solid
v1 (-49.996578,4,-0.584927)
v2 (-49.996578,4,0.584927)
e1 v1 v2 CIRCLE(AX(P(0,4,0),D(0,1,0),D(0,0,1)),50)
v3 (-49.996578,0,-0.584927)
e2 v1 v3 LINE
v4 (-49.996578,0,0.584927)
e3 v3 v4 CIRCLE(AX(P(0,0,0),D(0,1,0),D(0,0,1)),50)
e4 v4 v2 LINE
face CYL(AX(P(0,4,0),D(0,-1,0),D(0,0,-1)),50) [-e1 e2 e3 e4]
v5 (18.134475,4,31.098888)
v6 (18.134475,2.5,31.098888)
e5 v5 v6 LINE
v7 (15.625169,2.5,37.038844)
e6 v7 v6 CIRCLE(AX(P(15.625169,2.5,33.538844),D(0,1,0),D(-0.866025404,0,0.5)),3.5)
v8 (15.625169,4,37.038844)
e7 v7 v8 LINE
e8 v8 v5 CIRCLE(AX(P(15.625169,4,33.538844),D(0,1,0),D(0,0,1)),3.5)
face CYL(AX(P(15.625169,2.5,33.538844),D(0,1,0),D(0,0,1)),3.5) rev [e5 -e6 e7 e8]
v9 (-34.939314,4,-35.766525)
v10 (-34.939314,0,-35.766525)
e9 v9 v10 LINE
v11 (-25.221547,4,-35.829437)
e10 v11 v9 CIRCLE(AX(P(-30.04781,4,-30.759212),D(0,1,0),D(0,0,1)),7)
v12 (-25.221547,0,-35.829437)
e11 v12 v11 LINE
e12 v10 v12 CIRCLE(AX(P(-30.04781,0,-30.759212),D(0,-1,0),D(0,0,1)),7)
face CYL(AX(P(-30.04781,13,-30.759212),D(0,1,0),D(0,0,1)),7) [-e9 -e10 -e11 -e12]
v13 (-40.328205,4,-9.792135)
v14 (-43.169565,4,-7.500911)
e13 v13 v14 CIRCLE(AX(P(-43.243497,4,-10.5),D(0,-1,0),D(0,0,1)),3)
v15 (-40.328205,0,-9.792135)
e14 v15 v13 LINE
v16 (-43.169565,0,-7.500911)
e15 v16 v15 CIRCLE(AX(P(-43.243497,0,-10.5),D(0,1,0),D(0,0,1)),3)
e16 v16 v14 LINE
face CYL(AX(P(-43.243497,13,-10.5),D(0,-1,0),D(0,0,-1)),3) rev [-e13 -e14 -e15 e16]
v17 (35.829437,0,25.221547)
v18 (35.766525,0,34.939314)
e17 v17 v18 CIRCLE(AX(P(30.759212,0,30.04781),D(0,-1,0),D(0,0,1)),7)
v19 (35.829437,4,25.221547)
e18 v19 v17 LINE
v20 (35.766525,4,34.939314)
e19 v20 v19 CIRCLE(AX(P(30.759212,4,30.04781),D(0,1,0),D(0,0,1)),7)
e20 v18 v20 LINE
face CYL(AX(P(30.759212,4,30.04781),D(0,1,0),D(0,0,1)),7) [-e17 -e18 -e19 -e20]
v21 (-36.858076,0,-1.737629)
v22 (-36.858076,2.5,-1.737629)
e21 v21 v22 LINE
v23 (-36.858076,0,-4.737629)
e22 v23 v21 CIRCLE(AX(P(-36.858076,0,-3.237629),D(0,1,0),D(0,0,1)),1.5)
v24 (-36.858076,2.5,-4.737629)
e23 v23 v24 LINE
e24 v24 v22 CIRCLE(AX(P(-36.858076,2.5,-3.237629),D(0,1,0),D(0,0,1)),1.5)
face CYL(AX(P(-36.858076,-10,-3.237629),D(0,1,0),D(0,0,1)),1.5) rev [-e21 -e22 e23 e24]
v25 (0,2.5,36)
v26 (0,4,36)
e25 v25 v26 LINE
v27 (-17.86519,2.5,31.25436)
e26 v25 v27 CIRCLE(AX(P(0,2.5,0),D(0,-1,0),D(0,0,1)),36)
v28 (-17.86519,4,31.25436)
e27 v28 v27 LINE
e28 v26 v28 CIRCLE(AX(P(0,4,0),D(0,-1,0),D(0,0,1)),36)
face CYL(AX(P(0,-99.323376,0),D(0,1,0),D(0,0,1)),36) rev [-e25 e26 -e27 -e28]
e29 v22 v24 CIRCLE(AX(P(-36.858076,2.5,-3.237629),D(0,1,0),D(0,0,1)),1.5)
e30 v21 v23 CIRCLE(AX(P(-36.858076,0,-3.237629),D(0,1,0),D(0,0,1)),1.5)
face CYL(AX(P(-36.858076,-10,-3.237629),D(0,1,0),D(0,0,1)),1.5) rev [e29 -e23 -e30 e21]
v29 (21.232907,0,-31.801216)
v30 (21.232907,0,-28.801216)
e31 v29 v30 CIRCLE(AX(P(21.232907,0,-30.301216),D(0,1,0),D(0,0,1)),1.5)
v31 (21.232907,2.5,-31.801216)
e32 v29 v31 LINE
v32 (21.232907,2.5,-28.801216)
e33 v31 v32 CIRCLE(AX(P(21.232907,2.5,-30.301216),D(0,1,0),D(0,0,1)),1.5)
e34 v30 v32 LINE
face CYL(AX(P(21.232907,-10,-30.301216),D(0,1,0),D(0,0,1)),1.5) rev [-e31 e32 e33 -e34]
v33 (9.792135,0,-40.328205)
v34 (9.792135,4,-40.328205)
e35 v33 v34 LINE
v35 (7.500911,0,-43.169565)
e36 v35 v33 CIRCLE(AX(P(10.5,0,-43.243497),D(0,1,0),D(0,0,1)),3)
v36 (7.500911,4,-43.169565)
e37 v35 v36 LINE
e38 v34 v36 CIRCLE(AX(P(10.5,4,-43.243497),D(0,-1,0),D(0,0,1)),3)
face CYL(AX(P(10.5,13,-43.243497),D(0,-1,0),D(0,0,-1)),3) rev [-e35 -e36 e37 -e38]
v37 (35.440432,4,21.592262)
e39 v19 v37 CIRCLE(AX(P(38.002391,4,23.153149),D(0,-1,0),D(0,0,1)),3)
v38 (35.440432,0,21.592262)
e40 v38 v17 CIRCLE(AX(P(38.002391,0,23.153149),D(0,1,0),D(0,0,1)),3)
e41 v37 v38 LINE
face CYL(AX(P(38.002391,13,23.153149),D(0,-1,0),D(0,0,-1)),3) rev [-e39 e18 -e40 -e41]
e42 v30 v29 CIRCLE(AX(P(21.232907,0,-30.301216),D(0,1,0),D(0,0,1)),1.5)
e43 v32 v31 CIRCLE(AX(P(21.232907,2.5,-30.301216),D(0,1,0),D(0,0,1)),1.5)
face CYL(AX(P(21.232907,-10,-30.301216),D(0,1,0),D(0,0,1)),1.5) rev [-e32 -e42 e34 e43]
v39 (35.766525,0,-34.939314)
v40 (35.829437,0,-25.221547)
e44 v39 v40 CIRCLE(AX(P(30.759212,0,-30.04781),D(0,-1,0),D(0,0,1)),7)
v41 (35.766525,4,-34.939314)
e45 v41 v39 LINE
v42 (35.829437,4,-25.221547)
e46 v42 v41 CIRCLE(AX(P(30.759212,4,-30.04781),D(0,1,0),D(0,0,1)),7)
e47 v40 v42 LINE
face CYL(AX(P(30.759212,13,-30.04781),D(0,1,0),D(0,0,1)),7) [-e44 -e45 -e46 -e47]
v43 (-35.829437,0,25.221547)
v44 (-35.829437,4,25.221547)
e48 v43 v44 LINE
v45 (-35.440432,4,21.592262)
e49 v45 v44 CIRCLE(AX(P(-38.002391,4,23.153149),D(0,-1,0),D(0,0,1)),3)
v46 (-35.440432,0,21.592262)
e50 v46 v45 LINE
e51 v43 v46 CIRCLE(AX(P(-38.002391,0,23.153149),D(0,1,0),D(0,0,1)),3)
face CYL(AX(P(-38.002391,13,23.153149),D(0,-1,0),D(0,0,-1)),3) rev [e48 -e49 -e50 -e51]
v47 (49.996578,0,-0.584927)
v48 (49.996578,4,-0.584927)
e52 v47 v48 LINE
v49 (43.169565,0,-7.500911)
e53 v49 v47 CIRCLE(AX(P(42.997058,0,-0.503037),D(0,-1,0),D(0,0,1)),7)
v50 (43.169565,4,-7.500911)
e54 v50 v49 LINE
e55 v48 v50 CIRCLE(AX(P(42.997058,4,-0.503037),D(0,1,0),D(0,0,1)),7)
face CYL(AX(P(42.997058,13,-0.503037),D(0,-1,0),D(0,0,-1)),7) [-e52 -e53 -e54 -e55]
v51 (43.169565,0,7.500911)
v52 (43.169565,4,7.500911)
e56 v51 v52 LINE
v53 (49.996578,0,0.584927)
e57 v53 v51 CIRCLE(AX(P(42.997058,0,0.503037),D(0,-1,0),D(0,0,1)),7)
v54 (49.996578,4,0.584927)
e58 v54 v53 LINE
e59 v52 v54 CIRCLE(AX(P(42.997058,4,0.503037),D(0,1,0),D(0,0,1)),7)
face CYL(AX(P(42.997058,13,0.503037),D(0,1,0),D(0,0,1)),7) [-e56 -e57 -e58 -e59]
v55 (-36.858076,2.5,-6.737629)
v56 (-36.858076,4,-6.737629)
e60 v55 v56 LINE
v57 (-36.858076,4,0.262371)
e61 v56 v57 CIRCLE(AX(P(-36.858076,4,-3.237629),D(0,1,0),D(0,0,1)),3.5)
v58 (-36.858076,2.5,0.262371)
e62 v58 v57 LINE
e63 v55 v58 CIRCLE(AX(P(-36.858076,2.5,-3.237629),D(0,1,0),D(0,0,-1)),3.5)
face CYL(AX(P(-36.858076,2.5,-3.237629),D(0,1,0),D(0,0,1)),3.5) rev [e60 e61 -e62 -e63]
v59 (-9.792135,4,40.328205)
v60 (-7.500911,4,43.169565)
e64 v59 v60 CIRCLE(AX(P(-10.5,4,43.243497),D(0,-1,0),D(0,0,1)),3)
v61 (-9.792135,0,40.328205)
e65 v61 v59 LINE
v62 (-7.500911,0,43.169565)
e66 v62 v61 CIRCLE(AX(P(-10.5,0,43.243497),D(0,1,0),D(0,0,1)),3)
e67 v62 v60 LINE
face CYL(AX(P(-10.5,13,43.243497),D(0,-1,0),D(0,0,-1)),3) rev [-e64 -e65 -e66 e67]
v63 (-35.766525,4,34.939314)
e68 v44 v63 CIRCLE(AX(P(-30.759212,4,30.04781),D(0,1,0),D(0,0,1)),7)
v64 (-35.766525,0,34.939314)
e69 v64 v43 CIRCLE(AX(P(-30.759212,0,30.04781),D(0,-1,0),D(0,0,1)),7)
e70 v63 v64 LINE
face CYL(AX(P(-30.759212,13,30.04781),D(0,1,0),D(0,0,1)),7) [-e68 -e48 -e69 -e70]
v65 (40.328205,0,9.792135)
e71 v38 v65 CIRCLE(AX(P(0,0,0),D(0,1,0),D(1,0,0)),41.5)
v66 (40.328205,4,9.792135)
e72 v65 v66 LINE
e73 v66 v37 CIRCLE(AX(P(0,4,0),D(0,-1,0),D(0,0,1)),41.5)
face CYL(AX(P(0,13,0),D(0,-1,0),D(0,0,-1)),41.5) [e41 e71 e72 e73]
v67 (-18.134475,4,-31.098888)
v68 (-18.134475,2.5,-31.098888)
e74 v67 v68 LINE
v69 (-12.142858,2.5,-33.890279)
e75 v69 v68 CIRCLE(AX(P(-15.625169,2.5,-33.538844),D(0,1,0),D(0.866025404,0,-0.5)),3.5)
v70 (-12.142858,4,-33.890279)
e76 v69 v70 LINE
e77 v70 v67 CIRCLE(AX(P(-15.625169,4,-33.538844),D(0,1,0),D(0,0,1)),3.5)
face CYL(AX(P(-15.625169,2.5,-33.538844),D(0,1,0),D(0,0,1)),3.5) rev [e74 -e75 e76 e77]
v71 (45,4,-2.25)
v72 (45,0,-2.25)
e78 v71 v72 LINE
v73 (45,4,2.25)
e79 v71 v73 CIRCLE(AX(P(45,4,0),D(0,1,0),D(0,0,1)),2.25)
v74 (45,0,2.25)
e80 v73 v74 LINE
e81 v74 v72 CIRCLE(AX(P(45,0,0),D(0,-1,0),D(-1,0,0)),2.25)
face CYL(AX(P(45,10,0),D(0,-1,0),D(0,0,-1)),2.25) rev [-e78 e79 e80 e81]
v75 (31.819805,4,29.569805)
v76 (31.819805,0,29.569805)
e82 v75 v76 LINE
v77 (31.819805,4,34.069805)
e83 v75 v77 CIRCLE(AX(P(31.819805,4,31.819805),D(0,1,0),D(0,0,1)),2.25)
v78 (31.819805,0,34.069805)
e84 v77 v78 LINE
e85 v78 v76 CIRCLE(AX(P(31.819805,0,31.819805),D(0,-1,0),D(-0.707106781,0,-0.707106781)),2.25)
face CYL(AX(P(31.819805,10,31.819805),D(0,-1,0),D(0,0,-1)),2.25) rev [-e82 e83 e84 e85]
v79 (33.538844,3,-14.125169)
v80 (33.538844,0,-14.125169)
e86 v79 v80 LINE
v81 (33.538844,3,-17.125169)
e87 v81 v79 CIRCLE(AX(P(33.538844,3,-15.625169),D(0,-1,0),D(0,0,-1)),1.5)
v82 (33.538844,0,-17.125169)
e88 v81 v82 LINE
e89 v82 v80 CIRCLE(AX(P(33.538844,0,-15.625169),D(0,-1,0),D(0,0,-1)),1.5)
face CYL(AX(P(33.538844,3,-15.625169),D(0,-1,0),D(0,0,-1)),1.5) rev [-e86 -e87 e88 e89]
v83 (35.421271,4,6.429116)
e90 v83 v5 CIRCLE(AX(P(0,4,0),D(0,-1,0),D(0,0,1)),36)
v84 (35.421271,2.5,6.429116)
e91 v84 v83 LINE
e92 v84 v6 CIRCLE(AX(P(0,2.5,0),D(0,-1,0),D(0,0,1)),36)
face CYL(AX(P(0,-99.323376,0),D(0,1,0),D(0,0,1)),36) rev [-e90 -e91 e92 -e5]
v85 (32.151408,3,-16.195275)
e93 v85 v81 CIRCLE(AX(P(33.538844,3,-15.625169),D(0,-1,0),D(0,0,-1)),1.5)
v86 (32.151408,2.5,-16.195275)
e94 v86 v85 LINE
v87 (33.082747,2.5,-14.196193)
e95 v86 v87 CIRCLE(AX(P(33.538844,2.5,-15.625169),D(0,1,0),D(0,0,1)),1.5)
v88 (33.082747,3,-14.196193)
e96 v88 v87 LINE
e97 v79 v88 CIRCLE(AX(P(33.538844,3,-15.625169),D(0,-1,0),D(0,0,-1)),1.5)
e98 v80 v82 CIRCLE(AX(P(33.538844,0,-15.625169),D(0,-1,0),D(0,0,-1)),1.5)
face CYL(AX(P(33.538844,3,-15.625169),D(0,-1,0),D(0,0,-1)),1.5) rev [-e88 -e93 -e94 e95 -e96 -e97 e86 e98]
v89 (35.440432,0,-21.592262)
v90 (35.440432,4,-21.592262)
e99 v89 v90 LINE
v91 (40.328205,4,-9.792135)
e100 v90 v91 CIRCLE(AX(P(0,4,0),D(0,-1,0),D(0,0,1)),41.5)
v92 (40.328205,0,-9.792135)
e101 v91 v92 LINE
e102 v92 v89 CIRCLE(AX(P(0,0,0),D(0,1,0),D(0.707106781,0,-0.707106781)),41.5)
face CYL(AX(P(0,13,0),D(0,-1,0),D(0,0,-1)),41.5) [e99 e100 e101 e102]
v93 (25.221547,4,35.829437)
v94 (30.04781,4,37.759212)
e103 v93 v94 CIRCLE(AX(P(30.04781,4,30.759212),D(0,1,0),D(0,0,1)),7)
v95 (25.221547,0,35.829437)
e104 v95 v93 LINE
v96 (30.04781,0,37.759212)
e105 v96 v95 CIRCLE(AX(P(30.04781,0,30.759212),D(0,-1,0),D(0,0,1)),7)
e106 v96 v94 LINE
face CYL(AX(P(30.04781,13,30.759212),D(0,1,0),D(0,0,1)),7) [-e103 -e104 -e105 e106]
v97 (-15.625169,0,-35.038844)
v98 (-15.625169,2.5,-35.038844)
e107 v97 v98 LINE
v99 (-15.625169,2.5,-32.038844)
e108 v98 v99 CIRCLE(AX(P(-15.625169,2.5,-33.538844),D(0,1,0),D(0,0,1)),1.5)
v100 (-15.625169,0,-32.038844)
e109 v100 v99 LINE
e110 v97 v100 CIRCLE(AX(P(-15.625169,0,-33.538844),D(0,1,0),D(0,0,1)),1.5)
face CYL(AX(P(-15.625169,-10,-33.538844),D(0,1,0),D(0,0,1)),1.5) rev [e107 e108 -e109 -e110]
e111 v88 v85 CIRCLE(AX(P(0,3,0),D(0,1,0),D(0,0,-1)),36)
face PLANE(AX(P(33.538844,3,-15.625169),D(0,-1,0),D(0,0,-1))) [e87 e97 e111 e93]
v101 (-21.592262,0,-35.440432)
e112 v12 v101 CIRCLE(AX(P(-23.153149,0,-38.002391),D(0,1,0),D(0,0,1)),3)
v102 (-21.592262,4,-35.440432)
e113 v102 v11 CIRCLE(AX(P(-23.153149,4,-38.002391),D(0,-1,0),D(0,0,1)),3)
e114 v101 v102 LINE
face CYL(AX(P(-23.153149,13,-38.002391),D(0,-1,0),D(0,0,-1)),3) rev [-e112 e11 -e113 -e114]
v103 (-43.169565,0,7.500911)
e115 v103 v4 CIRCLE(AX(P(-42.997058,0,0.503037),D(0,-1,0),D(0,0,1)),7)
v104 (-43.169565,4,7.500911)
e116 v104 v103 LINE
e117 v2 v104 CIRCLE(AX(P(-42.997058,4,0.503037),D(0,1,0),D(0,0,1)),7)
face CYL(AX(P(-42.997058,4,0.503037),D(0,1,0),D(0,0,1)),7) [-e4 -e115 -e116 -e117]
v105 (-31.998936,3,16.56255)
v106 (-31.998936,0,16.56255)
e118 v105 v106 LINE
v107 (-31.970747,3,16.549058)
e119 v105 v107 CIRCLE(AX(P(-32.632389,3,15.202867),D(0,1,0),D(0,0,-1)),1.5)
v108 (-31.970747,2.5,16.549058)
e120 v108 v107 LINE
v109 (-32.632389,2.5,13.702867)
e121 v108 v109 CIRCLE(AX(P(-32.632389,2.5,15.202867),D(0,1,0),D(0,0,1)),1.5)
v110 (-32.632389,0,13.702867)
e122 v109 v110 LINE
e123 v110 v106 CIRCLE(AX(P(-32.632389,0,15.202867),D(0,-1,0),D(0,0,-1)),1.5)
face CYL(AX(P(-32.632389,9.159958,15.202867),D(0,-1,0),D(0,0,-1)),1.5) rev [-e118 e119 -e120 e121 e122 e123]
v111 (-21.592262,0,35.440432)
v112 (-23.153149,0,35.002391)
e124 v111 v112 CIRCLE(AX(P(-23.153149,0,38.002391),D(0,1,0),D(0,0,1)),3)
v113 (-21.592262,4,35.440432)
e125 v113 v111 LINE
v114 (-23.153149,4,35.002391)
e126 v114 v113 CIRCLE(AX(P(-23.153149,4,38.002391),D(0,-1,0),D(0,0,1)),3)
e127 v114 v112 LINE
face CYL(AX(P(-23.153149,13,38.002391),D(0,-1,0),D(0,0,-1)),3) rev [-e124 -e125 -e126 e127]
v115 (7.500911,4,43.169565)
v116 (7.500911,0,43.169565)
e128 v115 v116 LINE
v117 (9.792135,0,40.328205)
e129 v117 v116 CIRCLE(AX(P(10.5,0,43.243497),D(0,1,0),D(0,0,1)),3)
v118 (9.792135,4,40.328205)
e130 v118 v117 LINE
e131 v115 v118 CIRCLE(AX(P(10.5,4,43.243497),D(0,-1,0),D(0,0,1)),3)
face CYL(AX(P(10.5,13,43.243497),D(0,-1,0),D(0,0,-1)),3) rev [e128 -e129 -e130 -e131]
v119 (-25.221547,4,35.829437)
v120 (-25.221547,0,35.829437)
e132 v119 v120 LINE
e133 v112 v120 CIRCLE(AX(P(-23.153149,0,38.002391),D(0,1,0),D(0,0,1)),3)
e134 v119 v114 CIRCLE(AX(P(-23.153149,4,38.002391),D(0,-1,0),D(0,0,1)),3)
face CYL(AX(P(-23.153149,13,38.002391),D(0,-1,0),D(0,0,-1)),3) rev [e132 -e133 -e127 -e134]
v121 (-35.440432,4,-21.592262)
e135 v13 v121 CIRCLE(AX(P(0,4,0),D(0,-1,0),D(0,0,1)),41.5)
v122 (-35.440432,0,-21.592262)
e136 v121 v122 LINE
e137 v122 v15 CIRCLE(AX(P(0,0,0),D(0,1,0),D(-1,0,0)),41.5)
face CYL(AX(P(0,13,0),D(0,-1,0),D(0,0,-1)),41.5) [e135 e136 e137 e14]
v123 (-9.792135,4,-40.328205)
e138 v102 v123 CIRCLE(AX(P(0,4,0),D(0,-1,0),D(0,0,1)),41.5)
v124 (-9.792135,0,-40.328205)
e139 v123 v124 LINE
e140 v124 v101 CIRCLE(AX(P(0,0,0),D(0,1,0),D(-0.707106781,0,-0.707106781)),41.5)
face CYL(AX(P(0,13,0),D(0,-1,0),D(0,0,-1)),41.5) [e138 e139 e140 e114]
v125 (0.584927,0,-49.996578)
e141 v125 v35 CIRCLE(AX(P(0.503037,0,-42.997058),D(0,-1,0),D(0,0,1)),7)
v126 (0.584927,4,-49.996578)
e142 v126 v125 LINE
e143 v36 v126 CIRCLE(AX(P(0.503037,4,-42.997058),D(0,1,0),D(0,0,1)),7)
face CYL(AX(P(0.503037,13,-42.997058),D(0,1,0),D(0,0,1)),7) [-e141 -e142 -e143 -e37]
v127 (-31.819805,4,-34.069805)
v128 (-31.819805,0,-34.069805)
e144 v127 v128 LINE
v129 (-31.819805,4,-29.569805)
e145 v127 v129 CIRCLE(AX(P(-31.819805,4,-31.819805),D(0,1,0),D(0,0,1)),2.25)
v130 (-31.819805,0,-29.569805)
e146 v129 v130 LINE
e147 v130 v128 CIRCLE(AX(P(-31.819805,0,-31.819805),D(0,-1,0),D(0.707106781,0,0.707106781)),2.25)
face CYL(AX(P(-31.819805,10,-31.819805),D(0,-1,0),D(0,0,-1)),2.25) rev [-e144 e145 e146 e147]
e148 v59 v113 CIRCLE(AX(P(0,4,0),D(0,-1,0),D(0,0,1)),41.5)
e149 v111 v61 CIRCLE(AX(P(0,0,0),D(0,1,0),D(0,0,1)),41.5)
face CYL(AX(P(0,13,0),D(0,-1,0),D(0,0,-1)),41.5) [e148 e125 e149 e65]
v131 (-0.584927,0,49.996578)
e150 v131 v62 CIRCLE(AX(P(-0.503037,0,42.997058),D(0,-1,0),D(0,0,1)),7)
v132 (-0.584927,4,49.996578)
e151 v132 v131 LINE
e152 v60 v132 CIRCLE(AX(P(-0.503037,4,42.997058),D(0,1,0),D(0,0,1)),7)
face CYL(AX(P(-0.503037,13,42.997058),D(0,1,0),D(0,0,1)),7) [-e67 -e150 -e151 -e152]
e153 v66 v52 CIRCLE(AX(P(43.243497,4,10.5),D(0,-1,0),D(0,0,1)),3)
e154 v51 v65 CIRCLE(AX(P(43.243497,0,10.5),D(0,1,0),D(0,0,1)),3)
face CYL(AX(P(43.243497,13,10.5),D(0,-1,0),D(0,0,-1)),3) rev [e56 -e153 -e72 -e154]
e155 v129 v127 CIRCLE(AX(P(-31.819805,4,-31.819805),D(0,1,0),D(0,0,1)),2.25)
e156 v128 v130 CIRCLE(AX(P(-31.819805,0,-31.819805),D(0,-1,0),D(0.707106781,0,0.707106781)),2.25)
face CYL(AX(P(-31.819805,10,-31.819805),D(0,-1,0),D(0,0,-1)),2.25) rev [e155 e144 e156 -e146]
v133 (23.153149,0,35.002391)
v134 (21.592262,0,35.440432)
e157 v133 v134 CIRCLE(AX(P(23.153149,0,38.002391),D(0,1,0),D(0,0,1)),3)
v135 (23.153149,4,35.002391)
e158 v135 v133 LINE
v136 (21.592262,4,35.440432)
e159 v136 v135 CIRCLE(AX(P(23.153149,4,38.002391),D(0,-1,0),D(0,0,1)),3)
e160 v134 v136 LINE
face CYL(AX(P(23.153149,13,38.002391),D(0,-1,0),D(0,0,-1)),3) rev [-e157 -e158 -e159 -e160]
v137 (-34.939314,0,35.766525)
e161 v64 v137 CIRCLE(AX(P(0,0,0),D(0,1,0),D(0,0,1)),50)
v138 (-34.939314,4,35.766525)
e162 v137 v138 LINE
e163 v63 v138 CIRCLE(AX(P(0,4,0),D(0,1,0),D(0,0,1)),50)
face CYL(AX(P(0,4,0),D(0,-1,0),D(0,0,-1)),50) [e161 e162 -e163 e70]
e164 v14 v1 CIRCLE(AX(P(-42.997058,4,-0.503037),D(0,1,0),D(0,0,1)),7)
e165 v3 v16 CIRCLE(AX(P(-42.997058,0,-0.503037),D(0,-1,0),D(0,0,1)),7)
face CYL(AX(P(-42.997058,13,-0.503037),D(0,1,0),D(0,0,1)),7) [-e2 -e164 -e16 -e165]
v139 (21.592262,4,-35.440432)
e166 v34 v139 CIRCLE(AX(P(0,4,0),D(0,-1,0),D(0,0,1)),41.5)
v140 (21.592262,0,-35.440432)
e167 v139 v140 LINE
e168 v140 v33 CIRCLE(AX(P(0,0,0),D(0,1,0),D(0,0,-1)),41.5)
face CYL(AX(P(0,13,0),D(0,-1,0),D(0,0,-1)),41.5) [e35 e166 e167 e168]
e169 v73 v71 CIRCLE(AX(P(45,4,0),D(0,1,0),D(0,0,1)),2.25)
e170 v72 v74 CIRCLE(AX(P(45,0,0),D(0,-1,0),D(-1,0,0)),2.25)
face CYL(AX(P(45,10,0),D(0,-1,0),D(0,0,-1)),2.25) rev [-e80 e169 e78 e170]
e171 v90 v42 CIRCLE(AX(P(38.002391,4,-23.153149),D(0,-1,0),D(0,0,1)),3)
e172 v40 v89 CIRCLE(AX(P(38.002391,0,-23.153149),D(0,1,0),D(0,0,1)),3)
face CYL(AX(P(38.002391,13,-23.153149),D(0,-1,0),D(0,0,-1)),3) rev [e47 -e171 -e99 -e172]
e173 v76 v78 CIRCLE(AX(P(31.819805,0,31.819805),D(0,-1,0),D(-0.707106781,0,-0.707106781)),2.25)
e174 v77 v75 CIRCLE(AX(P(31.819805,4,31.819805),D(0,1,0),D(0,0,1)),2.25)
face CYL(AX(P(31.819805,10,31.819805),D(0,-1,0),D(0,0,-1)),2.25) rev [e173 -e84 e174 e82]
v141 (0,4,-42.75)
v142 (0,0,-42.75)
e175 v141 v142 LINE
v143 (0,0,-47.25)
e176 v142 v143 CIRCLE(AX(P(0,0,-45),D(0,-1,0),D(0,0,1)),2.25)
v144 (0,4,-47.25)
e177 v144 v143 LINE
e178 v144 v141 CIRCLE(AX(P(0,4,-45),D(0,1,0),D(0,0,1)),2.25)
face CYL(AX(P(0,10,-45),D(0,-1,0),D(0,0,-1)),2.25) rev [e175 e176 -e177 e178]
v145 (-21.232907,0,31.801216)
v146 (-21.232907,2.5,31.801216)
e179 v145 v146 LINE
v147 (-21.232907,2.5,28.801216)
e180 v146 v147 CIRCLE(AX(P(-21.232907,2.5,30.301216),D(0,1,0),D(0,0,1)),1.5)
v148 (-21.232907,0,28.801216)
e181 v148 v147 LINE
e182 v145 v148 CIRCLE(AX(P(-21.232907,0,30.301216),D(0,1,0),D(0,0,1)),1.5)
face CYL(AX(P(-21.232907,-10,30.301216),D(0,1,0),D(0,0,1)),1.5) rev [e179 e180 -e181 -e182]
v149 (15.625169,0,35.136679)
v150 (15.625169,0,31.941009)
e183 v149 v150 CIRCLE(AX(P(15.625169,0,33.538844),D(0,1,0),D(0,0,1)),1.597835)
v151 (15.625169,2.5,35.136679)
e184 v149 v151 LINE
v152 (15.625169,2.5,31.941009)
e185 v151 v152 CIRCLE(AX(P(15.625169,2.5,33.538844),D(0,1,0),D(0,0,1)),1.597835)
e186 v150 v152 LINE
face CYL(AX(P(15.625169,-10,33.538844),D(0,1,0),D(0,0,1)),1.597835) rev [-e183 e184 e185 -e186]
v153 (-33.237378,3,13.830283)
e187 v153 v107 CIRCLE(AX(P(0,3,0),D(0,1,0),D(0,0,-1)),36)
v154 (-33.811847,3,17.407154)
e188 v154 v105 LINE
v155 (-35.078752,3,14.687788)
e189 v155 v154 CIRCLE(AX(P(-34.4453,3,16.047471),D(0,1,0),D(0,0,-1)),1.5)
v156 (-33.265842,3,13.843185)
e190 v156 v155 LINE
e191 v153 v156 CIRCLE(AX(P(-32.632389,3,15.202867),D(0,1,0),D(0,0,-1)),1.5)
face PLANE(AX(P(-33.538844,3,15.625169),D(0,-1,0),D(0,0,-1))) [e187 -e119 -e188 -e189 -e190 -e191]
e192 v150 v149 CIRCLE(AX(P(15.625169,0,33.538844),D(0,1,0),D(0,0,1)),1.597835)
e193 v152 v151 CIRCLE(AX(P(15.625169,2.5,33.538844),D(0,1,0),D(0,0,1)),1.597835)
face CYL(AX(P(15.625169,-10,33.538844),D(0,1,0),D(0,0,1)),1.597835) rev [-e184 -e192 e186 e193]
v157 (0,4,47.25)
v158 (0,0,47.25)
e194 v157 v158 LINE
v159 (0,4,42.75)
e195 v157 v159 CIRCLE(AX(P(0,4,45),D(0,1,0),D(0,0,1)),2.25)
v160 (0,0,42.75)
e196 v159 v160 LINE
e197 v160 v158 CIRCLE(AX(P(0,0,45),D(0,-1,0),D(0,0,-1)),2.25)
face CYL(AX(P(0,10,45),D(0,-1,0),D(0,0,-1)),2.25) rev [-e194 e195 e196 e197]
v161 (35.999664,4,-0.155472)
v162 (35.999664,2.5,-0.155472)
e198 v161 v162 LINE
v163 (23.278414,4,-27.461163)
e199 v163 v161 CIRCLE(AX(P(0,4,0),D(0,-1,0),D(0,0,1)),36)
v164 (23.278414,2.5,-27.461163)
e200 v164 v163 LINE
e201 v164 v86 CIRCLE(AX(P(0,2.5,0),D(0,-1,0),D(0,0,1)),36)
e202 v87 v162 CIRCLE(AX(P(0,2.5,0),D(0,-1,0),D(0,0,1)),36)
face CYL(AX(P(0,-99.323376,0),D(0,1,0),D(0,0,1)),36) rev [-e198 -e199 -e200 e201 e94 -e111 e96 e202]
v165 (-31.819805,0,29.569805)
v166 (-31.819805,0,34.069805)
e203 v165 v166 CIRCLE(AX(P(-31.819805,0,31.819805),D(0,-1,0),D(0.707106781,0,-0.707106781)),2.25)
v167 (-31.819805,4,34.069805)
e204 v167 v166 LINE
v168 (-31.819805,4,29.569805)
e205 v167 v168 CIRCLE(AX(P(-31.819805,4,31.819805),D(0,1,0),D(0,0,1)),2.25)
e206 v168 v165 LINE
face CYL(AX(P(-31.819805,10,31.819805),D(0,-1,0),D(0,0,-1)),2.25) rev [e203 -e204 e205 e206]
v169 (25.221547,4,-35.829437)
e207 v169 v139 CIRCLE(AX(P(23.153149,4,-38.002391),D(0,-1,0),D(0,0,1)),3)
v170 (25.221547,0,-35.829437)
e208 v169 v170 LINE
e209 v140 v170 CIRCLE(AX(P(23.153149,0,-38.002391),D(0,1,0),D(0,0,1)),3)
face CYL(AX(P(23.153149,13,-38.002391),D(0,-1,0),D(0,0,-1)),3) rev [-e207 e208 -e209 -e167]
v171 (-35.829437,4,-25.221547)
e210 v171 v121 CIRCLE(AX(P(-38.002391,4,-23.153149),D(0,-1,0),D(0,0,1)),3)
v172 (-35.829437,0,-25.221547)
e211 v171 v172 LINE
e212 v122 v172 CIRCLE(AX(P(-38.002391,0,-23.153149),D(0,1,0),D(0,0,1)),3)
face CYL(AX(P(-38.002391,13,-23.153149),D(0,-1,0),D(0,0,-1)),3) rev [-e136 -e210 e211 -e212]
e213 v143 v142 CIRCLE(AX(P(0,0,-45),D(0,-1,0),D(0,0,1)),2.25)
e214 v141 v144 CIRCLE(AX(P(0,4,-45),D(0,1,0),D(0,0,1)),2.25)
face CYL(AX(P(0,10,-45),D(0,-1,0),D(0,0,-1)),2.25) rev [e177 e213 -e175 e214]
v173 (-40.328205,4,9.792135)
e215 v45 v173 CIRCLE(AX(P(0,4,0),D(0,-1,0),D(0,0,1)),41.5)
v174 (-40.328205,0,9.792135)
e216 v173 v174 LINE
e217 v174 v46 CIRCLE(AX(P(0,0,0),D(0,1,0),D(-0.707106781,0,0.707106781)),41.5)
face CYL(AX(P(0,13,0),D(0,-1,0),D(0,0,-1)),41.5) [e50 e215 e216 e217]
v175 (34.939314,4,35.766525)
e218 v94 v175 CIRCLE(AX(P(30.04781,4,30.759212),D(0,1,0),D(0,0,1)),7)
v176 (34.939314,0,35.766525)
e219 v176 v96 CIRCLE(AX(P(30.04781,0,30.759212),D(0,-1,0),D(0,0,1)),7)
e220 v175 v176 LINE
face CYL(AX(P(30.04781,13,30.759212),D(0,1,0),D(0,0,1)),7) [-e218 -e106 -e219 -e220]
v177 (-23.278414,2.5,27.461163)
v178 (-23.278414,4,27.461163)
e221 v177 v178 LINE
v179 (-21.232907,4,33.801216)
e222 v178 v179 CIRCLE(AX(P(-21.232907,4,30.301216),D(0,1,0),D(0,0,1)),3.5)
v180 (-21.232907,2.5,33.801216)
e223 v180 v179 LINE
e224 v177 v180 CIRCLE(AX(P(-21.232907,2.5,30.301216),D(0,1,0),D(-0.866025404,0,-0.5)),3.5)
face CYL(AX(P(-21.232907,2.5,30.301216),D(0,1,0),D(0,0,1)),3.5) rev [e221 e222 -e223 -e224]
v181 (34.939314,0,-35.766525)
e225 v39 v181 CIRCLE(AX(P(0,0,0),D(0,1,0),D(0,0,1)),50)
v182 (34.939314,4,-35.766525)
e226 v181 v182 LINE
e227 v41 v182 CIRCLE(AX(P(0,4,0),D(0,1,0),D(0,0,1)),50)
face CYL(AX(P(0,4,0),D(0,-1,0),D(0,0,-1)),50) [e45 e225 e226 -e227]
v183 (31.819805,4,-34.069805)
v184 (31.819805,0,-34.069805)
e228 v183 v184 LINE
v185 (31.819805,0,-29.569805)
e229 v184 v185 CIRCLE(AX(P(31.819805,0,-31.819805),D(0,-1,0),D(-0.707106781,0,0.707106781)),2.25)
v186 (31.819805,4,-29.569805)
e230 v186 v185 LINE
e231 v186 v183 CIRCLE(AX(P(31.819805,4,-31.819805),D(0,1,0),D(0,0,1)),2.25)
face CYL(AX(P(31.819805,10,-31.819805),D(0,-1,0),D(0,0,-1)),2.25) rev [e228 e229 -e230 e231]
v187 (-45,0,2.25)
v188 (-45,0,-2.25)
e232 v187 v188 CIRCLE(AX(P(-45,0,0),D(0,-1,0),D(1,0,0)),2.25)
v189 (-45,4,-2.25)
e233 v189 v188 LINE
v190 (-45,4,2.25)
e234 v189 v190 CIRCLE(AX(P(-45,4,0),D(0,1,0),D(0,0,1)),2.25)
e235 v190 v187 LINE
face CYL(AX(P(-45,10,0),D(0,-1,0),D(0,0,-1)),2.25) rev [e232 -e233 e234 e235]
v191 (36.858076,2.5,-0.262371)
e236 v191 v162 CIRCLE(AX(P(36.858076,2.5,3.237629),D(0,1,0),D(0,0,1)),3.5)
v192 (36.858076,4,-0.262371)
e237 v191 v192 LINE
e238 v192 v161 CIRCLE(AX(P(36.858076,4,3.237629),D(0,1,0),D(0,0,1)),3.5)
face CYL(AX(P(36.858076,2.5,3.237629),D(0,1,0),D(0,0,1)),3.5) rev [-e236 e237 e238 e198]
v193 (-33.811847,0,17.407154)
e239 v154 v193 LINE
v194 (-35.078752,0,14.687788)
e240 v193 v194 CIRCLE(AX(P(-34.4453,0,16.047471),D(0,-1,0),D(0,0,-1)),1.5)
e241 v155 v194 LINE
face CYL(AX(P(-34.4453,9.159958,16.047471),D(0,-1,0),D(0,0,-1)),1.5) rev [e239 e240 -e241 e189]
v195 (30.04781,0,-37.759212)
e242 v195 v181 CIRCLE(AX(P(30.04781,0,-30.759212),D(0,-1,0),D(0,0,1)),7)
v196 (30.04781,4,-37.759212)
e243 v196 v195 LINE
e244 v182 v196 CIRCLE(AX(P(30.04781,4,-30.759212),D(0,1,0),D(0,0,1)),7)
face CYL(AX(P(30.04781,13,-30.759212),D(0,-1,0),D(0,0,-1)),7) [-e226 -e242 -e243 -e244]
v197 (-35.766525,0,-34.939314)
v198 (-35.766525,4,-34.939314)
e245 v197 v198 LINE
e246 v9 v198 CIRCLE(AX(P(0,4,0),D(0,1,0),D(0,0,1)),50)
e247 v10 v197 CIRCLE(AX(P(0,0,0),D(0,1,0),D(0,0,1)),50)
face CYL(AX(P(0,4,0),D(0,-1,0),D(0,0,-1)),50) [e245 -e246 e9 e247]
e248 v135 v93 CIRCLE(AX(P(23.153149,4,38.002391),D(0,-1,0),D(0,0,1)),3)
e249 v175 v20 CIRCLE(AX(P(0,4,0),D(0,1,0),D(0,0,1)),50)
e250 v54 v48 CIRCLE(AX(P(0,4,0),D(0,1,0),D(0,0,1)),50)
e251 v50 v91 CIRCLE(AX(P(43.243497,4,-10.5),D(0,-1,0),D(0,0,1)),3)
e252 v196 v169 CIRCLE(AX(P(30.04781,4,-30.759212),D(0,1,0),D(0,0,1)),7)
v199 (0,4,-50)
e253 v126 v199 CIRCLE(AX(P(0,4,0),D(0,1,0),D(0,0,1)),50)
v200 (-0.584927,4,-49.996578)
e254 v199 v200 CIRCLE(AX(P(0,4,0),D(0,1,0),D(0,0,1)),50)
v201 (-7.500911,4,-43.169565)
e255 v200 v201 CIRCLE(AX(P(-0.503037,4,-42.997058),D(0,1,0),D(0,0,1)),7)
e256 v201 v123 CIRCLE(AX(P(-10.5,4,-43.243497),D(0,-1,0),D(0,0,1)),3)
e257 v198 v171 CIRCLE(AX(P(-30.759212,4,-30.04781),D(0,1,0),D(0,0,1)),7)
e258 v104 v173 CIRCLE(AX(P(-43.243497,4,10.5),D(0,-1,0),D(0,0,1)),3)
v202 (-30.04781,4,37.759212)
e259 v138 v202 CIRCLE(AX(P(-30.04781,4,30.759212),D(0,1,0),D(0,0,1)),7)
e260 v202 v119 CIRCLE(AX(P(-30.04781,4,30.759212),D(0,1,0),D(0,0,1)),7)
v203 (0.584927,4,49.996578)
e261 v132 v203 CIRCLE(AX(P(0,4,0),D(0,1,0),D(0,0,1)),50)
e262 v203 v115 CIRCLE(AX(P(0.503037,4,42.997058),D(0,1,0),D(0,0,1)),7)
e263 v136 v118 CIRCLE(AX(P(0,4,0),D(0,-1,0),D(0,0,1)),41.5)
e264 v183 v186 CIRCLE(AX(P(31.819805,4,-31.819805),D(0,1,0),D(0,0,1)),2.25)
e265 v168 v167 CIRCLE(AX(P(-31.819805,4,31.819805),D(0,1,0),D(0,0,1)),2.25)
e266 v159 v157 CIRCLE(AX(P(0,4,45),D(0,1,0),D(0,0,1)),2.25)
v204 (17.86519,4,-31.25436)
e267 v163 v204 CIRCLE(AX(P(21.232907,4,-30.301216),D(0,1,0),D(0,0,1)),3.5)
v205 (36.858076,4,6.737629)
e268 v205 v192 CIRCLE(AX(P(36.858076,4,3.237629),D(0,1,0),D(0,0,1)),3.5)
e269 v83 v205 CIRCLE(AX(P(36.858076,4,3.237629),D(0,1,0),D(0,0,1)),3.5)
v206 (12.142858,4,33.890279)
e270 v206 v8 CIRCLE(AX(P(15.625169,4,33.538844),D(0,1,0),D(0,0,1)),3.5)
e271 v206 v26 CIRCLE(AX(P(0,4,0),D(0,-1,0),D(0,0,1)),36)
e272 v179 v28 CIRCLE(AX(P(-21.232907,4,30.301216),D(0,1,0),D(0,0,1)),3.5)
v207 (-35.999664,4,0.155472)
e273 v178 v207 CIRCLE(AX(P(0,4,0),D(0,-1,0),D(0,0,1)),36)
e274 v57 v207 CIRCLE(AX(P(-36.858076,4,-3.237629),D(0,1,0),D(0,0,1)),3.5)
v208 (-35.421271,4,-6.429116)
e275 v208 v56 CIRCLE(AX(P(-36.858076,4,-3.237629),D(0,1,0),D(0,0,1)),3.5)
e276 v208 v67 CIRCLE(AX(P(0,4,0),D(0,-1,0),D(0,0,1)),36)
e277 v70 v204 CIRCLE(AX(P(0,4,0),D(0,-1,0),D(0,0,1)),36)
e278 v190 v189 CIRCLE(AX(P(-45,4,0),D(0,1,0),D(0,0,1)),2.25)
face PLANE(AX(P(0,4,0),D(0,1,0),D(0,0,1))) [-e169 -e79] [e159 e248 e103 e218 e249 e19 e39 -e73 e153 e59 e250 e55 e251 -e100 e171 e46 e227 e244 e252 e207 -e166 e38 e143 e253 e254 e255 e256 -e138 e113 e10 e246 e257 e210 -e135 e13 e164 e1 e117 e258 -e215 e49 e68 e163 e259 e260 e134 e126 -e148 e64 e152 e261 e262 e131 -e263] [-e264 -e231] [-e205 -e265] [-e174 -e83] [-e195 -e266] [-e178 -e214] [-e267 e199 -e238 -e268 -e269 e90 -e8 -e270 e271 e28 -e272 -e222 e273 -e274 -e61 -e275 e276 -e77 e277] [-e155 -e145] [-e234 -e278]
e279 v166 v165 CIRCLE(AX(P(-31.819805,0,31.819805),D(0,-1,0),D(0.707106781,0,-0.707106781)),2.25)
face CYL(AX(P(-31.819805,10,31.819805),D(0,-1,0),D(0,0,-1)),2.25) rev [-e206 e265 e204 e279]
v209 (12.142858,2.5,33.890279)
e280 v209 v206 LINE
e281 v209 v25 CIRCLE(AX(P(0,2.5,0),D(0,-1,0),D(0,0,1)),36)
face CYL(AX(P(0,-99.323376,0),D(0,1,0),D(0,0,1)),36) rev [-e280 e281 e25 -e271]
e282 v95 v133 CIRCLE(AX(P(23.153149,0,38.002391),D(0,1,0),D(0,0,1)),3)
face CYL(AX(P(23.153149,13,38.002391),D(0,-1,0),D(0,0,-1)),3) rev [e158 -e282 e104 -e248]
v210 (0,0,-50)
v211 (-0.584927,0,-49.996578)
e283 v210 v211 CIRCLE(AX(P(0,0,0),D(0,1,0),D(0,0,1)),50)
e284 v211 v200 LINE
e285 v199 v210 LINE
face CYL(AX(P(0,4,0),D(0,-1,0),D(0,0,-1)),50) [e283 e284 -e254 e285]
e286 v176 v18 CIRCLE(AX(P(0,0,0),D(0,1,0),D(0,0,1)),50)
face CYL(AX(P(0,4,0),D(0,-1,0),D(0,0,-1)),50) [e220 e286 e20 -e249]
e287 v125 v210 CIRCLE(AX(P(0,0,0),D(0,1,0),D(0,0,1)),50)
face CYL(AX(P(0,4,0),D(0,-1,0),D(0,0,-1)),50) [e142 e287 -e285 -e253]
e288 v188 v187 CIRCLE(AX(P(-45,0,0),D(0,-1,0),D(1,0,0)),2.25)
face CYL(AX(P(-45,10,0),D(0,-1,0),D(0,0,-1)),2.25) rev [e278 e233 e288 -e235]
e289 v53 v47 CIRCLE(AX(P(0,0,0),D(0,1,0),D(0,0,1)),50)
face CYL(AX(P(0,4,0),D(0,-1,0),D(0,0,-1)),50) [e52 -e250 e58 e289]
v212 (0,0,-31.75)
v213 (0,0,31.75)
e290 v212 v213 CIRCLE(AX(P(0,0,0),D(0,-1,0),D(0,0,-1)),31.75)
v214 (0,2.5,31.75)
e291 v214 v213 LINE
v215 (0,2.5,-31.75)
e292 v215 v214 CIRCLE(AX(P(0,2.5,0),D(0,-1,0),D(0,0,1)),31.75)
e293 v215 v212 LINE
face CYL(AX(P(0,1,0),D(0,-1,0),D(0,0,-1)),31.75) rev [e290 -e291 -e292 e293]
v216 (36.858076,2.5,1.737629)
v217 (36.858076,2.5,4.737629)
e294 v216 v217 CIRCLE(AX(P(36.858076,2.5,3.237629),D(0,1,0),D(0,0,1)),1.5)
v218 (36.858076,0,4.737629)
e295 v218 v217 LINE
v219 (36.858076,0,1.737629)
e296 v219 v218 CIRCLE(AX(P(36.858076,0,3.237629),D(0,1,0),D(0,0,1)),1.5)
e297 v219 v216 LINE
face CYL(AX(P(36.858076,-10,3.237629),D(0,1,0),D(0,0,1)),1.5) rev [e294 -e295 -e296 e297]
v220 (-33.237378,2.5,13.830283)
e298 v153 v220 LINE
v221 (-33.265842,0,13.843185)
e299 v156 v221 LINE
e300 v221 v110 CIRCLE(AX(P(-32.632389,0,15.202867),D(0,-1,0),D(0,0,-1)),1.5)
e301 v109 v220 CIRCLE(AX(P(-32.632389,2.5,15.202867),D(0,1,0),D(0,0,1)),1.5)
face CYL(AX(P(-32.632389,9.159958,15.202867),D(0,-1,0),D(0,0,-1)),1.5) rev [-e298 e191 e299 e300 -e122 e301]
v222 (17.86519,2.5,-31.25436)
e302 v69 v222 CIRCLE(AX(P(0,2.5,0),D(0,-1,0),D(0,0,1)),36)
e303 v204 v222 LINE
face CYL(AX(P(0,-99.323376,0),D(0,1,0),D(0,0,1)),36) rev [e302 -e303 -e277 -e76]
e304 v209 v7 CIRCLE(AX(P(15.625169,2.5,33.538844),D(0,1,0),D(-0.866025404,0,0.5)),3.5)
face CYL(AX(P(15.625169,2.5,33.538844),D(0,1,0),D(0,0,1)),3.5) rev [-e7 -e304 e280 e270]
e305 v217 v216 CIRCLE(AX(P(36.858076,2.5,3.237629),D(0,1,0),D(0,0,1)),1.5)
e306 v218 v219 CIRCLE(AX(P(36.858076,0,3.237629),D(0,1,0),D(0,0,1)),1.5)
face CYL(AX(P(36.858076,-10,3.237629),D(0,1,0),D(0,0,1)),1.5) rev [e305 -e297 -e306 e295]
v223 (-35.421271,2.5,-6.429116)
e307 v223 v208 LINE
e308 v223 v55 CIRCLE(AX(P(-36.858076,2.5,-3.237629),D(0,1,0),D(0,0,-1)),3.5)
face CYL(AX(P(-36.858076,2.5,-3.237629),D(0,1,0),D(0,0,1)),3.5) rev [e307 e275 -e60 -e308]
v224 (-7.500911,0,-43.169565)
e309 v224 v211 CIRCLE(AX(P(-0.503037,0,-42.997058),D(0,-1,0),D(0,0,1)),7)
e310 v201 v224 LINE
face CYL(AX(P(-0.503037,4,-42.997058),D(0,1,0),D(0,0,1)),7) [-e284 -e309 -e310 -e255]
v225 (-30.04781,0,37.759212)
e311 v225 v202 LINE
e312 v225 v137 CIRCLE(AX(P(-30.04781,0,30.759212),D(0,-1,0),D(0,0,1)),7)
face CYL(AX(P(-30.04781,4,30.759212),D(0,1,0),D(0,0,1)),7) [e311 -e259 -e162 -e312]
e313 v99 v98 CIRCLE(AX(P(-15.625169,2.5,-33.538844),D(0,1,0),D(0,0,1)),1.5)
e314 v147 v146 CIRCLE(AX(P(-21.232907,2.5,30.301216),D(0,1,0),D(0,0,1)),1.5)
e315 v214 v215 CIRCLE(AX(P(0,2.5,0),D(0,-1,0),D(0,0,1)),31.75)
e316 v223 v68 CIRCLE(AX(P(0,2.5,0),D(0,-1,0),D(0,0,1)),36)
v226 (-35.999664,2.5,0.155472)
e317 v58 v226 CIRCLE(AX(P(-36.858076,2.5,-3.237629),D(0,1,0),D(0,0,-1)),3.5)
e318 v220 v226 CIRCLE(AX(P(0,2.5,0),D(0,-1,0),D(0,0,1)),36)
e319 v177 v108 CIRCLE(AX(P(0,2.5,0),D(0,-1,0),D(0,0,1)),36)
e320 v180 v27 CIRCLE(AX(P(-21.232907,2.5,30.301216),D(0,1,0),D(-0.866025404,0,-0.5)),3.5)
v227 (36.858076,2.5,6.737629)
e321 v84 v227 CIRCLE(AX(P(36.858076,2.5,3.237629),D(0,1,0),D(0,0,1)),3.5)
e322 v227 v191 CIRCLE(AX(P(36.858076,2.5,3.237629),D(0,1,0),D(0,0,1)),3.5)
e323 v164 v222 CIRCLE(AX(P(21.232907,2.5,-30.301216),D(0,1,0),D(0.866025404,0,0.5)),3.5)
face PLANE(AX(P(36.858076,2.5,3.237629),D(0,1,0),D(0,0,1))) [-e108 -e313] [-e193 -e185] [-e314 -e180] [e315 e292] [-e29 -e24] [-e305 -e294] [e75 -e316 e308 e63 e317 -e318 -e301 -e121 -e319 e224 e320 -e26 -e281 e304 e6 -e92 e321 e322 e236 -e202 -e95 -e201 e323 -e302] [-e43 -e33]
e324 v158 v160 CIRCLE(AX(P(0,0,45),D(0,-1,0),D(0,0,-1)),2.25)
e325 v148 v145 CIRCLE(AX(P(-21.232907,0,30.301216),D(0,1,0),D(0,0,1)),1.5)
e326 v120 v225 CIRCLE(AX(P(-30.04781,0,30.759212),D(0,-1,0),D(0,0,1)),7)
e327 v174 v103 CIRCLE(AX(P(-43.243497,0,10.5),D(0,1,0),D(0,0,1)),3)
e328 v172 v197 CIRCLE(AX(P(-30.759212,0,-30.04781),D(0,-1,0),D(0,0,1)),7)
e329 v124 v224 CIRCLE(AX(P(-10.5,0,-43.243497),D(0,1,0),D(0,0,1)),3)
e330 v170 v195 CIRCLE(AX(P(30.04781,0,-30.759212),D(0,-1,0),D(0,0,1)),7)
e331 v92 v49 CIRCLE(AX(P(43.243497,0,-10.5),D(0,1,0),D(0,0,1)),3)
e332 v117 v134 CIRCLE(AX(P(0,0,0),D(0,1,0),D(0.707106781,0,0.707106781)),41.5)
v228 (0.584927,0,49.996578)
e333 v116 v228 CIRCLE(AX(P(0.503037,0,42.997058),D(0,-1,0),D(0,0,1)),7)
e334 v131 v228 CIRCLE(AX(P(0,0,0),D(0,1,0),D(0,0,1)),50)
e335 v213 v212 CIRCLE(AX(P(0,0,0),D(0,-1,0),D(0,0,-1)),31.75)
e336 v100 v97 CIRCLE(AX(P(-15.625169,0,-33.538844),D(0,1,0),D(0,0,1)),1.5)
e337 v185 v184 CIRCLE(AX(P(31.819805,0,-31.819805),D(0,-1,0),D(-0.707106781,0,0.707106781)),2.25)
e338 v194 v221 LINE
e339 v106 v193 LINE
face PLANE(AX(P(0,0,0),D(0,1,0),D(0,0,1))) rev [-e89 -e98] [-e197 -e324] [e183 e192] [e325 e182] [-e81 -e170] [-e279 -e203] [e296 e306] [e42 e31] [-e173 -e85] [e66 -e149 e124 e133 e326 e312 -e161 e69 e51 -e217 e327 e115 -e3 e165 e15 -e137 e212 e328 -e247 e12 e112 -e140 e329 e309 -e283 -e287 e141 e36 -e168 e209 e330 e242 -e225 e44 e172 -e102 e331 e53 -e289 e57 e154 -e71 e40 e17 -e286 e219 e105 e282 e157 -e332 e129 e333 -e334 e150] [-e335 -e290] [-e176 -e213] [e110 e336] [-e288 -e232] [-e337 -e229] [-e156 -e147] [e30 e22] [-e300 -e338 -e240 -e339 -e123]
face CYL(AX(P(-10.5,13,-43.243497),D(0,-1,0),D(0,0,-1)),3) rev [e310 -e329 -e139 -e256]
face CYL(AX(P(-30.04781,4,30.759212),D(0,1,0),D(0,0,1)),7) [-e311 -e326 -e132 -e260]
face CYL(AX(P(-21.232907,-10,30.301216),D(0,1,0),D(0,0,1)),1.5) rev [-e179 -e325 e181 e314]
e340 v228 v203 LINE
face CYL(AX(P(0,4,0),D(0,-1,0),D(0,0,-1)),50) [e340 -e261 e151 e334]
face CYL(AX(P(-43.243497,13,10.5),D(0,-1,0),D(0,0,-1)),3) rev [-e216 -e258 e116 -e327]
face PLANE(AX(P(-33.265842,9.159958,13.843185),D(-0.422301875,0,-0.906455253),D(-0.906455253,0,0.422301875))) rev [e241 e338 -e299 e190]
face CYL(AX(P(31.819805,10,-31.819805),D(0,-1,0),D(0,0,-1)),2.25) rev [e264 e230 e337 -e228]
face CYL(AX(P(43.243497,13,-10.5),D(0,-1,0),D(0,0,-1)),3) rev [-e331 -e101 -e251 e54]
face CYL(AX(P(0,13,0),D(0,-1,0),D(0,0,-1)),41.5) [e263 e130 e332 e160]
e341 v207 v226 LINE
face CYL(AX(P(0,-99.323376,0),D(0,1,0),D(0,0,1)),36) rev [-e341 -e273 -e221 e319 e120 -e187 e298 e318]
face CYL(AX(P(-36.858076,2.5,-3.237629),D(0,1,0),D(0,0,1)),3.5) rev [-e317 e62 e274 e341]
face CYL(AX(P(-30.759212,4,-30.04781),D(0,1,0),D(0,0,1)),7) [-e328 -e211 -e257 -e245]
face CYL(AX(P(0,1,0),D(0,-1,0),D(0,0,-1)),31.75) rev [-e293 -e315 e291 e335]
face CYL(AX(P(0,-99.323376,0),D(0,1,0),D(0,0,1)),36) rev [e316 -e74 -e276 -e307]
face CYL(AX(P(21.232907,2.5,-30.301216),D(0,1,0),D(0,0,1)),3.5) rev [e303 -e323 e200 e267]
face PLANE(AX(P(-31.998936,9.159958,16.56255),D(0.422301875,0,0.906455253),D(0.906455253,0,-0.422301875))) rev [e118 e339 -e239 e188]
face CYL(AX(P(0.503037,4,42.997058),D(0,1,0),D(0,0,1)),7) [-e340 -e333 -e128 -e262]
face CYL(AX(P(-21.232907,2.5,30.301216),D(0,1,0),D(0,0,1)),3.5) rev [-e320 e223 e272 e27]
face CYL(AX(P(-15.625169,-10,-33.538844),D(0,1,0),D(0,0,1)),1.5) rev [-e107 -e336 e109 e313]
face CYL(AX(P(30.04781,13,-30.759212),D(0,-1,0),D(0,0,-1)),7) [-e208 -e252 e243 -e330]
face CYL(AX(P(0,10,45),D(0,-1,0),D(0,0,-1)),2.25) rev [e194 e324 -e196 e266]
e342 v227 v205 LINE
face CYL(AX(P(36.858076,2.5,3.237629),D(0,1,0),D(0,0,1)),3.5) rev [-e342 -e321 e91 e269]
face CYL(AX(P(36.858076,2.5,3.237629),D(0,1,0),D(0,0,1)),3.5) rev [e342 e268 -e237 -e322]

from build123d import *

# Parameters (mm, degrees)
SKETCH1_R           = 50
SKETCH1_R_2         = 30
BOSS_EXTRUDE1_DEPTH = 4
SKETCH2_R           = 39
SKETCH2_R_2         = 30
BOSS_EXTRUDE2_DEPTH = 1
SKETCH3_R           = 31.75
CUT_EXTRUDE1_DEPTH  = 1
SKETCH4_R           = 2.25
CUT_EXTRUDE2_DEPTH  = 10
CIRPATTERN1_COUNT   = 8
SKETCH5_R           = 31.75
CUT_EXTRUDE3_DEPTH  = 27
SKETCH6_R           = 3.5
CUT_EXTRUDE4_DEPTH  = 2.5
CIRPATTERN2_COUNT   = 6
SKETCH7_R           = 1.5
SKETCH7_R_2         = 1.597835056
CUT_EXTRUDE5_DEPTH  = 15
CUT_EXTRUDE6_DEPTH  = 13
CIRPATTERN3_COUNT   = 8
FILLET1_R           = 3
SKETCH9_R           = 36
CUT_EXTRUDE7_DEPTH  = 2.5
FILLET2_R           = 7
CUT_EXTRUDE8_START  = -1
SKETCH10_R          = 50
CUT_EXTRUDE8_DEPTH  = 1
SKETCH12_R          = 1.5
CUT_EXTRUDE9_DEPTH  = 3
CUT_EXTRUDE10_REACH = 72.824


with BuildPart() as part:
    # Sketch1 → Boss-Extrude1 (new body)
    with BuildSketch(Plane(origin=(0, 0, 0), x_dir=(1, 0, 0), z_dir=(0, 1, 0))):
        with Locations(Location((0, 0, 0), (0, 0, 270))):
            Circle(SKETCH1_R)
        with Locations(Location((0, 0, 0), (0, 0, 270))):
            Circle(SKETCH1_R_2, mode=Mode.SUBTRACT)
    extrude(amount=BOSS_EXTRUDE1_DEPTH)

    # Sketch2 → Boss-Extrude2 (add)
    with BuildSketch(Plane(origin=(0, 4, 0), x_dir=(1, 0, 0), z_dir=(0, 1, 0))):
        with Locations(Location((0, 0, 0), (0, 0, 270))):
            Circle(SKETCH2_R)
        with Locations(Location((0, 0, 0), (0, 0, 270))):
            Circle(SKETCH2_R_2, mode=Mode.SUBTRACT)
    extrude(amount=BOSS_EXTRUDE2_DEPTH)

    # Sketch3 → Cut-Extrude1 (cut)
    with BuildSketch(Plane.XZ):
        with Locations(Location((0, 0, 0), (0, 0, 270))):
            Circle(SKETCH3_R)
    extrude(amount=-CUT_EXTRUDE1_DEPTH, mode=Mode.SUBTRACT)

    # Sketch4 → Cut-Extrude2 (cut)
    with BuildSketch(Plane.XZ):
        with Locations(Location((0, 45, 0), (0, 0, 270))):
            Circle(SKETCH4_R)
    cut_extrude2 = extrude(amount=-CUT_EXTRUDE2_DEPTH, mode=Mode.SUBTRACT)

    # CirPattern1: Cut-Extrude2 ×8 about axis
    cirpattern1_axis = Axis((0, 0, 0), (0, 1, 0))
    for i in range(1, CIRPATTERN1_COUNT):
        add(cut_extrude2.rotate(cirpattern1_axis, i * 360 / CIRPATTERN1_COUNT), mode=Mode.SUBTRACT)

    # Sketch5 → Cut-Extrude3 (cut)
    with BuildSketch(Plane.XZ):
        with Locations(Location((0, 0, 0), (0, 0, 270))):
            Circle(SKETCH5_R)
    extrude(amount=-CUT_EXTRUDE3_DEPTH, mode=Mode.SUBTRACT)

    # Sketch6 → Cut-Extrude4 (cut)
    with BuildSketch(Plane(origin=(0, 5, 0), x_dir=(1, 0, 0), z_dir=(0, 1, 0))):
        with Locations(Location((36.858075929, -3.237628574, 0), (0, 0, 270))):
            Circle(SKETCH6_R)
    cut_extrude4 = extrude(amount=-CUT_EXTRUDE4_DEPTH, mode=Mode.SUBTRACT)

    # CirPattern2: Cut-Extrude4 ×6 about axis
    cirpattern2_axis = Axis((0, 0, 0), (0, 1, 0))
    for i in range(1, CIRPATTERN2_COUNT):
        add(cut_extrude4.rotate(cirpattern2_axis, i * 360 / CIRPATTERN2_COUNT), mode=Mode.SUBTRACT)

    # Sketch7 → Cut-Extrude5 (cut)
    with BuildSketch(Plane(origin=(0, 5, 0), x_dir=(1, 0, 0), z_dir=(0, 1, 0))):
        with Locations(Location((-21.232906558, -30.301215802, 0), (0, 0, 270))):
            Circle(SKETCH7_R)
        with Locations(Location((15.625169371, -33.538844377, 0), (0, 0, 270))):
            Circle(SKETCH7_R_2)
        with Locations(Location((36.858075929, -3.237628574, 0), (0, 0, 270))):
            Circle(SKETCH7_R)
        with Locations(Location((21.232906558, 30.301215802, 0), (0, 0, 270))):
            Circle(SKETCH7_R)
        with Locations(Location((-15.625169371, 33.538844377, 0), (0, 0, 270))):
            Circle(SKETCH7_R)
        with Locations(Location((-36.858075929, 3.237628574, 0), (0, 0, 270))):
            Circle(SKETCH7_R)
    extrude(amount=-CUT_EXTRUDE5_DEPTH, mode=Mode.SUBTRACT)

    # Sketch8 → Cut-Extrude6 (cut)
    with BuildSketch(Plane.XZ):
        with BuildLine():
            Line((7.5, -40.816663264), (7.5, -49.434299833))
            ThreePointArc((7.5, -49.434299833), (19.134171618, -46.193976626), (29.652027776, -40.258629494))
            Line((29.652027776, -40.258629494), (23.55843852, -34.165040238))
            ThreePointArc((23.55843852, -34.165040238), (15.881362443, -38.341000599), (7.5, -40.816663264))
        make_face()
    cut_extrude6 = extrude(amount=-CUT_EXTRUDE6_DEPTH, mode=Mode.SUBTRACT)

    # CirPattern3: Cut-Extrude6 ×8 about axis
    cirpattern3_axis = Axis((0, 0, 0), (0, 1, 0))
    for i in range(1, CIRPATTERN3_COUNT):
        add(cut_extrude6.rotate(cirpattern3_axis, i * 360 / CIRPATTERN3_COUNT), mode=Mode.SUBTRACT)

    # Fillet1
    fillet1_edges = [part.edges().sort_by_distance(p)[0] for p in [
        (7.5, 2, -40.816663264),
        (23.55843852, 2, -34.165040238),
        (34.165040238, 2, -23.55843852),
        (40.816663264, 2, -7.5),
        (40.816663264, 2, 7.5),
        (34.165040238, 2, 23.55843852),
        (23.55843852, 2, 34.165040238),
        (7.5, 2, 40.816663264),
        (-7.5, 2, 40.816663264),
        (-23.55843852, 2, 34.165040238),
        (-34.165040238, 2, 23.55843852),
        (-40.816663264, 2, 7.5),
        (-40.816663264, 2, -7.5),
        (-34.165040238, 2, -23.55843852),
        (-23.55843852, 2, -34.165040238),
        (-7.5, 2, -40.816663264),
    ]]
    fillet(fillet1_edges, radius=FILLET1_R)

    # Sketch9 → Cut-Extrude7 (cut)
    with BuildSketch(Plane(origin=(0, 5, 0), x_dir=(1, 0, 0), z_dir=(0, 1, 0))):
        Circle(SKETCH9_R)
    extrude(amount=-CUT_EXTRUDE7_DEPTH, mode=Mode.SUBTRACT)

    # Fillet2
    fillet2_edges = [part.edges().sort_by_distance(p)[0] for p in [
        (40.258629494, 2, -29.652027776),
        (29.652027776, 2, -40.258629494),
        (7.5, 2, -49.434299833),
        (-7.5, 2, -49.434299833),
        (-29.652027776, 2, -40.258629494),
        (-40.258629494, 2, -29.652027776),
        (-49.434299833, 2, -7.5),
        (-49.434299833, 2, 7.5),
        (-40.258629494, 2, 29.652027776),
        (-29.652027776, 2, 40.258629494),
        (-7.5, 2, 49.434299833),
        (7.5, 2, 49.434299833),
        (29.652027776, 2, 40.258629494),
        (40.258629494, 2, 29.652027776),
        (49.434299833, 2, 7.5),
        (49.434299833, 2, -7.5),
    ]]
    fillet(fillet2_edges, radius=FILLET2_R)

    # Sketch10 → Cut-Extrude8 (cut)
    with BuildSketch(Plane(origin=(0, 5, 0), x_dir=(1, 0, 0), z_dir=(0, 1, 0)).offset(CUT_EXTRUDE8_START)):
        Circle(SKETCH10_R)
    extrude(amount=CUT_EXTRUDE8_DEPTH, mode=Mode.SUBTRACT)

    # Sketch12 → Cut-Extrude9 (cut)
    with BuildSketch(Plane.XZ):
        with Locations(Location((-33.538844377, 15.625169371, 0), (0, 0, 270))):
            Circle(SKETCH12_R)
        with Locations(Location((33.538844377, -15.625169371, 0), (0, 0, 270))):
            Circle(SKETCH12_R)
    extrude(amount=-CUT_EXTRUDE9_DEPTH, mode=Mode.SUBTRACT)

    # Cut-Extrude10: up to this face of the body (flat: up to its plane)
    cut_extrude10_end = Plane(part.part.faces().sort_by_distance((-33.670920616, 3, 15.686701414))[0])
    # Sketch13 → Cut-Extrude10 (cut, up to the picked face)
    with BuildSketch(Plane.XZ, mode=Mode.PRIVATE) as cut_extrude10_sk1:
        with BuildLine():
            Line((-33.265841936, 13.843184616), (-35.078752442, 14.687788366))
            ThreePointArc((-35.078752442, 14.687788366), (-35.80498251, 16.680924059), (-33.811846818, 17.407154126))
            Line((-33.811846818, 17.407154126), (-31.998936311, 16.562550377))
            ThreePointArc((-31.998936311, 16.562550377), (-31.272706243, 14.569414684), (-33.265841936, 13.843184616))
        make_face()
    cut_extrude10_tool1 = split(extrude(cut_extrude10_sk1.sketch, amount=-CUT_EXTRUDE10_REACH, mode=Mode.PRIVATE), bisect_by=cut_extrude10_end, keep=Keep.BOTH, mode=Mode.PRIVATE)
    add(cut_extrude10_tool1.solids().sort_by(Axis((-33.538844, 0, 15.625169), (0, 1, 0)))[0], mode=Mode.SUBTRACT)


solid = part.part
